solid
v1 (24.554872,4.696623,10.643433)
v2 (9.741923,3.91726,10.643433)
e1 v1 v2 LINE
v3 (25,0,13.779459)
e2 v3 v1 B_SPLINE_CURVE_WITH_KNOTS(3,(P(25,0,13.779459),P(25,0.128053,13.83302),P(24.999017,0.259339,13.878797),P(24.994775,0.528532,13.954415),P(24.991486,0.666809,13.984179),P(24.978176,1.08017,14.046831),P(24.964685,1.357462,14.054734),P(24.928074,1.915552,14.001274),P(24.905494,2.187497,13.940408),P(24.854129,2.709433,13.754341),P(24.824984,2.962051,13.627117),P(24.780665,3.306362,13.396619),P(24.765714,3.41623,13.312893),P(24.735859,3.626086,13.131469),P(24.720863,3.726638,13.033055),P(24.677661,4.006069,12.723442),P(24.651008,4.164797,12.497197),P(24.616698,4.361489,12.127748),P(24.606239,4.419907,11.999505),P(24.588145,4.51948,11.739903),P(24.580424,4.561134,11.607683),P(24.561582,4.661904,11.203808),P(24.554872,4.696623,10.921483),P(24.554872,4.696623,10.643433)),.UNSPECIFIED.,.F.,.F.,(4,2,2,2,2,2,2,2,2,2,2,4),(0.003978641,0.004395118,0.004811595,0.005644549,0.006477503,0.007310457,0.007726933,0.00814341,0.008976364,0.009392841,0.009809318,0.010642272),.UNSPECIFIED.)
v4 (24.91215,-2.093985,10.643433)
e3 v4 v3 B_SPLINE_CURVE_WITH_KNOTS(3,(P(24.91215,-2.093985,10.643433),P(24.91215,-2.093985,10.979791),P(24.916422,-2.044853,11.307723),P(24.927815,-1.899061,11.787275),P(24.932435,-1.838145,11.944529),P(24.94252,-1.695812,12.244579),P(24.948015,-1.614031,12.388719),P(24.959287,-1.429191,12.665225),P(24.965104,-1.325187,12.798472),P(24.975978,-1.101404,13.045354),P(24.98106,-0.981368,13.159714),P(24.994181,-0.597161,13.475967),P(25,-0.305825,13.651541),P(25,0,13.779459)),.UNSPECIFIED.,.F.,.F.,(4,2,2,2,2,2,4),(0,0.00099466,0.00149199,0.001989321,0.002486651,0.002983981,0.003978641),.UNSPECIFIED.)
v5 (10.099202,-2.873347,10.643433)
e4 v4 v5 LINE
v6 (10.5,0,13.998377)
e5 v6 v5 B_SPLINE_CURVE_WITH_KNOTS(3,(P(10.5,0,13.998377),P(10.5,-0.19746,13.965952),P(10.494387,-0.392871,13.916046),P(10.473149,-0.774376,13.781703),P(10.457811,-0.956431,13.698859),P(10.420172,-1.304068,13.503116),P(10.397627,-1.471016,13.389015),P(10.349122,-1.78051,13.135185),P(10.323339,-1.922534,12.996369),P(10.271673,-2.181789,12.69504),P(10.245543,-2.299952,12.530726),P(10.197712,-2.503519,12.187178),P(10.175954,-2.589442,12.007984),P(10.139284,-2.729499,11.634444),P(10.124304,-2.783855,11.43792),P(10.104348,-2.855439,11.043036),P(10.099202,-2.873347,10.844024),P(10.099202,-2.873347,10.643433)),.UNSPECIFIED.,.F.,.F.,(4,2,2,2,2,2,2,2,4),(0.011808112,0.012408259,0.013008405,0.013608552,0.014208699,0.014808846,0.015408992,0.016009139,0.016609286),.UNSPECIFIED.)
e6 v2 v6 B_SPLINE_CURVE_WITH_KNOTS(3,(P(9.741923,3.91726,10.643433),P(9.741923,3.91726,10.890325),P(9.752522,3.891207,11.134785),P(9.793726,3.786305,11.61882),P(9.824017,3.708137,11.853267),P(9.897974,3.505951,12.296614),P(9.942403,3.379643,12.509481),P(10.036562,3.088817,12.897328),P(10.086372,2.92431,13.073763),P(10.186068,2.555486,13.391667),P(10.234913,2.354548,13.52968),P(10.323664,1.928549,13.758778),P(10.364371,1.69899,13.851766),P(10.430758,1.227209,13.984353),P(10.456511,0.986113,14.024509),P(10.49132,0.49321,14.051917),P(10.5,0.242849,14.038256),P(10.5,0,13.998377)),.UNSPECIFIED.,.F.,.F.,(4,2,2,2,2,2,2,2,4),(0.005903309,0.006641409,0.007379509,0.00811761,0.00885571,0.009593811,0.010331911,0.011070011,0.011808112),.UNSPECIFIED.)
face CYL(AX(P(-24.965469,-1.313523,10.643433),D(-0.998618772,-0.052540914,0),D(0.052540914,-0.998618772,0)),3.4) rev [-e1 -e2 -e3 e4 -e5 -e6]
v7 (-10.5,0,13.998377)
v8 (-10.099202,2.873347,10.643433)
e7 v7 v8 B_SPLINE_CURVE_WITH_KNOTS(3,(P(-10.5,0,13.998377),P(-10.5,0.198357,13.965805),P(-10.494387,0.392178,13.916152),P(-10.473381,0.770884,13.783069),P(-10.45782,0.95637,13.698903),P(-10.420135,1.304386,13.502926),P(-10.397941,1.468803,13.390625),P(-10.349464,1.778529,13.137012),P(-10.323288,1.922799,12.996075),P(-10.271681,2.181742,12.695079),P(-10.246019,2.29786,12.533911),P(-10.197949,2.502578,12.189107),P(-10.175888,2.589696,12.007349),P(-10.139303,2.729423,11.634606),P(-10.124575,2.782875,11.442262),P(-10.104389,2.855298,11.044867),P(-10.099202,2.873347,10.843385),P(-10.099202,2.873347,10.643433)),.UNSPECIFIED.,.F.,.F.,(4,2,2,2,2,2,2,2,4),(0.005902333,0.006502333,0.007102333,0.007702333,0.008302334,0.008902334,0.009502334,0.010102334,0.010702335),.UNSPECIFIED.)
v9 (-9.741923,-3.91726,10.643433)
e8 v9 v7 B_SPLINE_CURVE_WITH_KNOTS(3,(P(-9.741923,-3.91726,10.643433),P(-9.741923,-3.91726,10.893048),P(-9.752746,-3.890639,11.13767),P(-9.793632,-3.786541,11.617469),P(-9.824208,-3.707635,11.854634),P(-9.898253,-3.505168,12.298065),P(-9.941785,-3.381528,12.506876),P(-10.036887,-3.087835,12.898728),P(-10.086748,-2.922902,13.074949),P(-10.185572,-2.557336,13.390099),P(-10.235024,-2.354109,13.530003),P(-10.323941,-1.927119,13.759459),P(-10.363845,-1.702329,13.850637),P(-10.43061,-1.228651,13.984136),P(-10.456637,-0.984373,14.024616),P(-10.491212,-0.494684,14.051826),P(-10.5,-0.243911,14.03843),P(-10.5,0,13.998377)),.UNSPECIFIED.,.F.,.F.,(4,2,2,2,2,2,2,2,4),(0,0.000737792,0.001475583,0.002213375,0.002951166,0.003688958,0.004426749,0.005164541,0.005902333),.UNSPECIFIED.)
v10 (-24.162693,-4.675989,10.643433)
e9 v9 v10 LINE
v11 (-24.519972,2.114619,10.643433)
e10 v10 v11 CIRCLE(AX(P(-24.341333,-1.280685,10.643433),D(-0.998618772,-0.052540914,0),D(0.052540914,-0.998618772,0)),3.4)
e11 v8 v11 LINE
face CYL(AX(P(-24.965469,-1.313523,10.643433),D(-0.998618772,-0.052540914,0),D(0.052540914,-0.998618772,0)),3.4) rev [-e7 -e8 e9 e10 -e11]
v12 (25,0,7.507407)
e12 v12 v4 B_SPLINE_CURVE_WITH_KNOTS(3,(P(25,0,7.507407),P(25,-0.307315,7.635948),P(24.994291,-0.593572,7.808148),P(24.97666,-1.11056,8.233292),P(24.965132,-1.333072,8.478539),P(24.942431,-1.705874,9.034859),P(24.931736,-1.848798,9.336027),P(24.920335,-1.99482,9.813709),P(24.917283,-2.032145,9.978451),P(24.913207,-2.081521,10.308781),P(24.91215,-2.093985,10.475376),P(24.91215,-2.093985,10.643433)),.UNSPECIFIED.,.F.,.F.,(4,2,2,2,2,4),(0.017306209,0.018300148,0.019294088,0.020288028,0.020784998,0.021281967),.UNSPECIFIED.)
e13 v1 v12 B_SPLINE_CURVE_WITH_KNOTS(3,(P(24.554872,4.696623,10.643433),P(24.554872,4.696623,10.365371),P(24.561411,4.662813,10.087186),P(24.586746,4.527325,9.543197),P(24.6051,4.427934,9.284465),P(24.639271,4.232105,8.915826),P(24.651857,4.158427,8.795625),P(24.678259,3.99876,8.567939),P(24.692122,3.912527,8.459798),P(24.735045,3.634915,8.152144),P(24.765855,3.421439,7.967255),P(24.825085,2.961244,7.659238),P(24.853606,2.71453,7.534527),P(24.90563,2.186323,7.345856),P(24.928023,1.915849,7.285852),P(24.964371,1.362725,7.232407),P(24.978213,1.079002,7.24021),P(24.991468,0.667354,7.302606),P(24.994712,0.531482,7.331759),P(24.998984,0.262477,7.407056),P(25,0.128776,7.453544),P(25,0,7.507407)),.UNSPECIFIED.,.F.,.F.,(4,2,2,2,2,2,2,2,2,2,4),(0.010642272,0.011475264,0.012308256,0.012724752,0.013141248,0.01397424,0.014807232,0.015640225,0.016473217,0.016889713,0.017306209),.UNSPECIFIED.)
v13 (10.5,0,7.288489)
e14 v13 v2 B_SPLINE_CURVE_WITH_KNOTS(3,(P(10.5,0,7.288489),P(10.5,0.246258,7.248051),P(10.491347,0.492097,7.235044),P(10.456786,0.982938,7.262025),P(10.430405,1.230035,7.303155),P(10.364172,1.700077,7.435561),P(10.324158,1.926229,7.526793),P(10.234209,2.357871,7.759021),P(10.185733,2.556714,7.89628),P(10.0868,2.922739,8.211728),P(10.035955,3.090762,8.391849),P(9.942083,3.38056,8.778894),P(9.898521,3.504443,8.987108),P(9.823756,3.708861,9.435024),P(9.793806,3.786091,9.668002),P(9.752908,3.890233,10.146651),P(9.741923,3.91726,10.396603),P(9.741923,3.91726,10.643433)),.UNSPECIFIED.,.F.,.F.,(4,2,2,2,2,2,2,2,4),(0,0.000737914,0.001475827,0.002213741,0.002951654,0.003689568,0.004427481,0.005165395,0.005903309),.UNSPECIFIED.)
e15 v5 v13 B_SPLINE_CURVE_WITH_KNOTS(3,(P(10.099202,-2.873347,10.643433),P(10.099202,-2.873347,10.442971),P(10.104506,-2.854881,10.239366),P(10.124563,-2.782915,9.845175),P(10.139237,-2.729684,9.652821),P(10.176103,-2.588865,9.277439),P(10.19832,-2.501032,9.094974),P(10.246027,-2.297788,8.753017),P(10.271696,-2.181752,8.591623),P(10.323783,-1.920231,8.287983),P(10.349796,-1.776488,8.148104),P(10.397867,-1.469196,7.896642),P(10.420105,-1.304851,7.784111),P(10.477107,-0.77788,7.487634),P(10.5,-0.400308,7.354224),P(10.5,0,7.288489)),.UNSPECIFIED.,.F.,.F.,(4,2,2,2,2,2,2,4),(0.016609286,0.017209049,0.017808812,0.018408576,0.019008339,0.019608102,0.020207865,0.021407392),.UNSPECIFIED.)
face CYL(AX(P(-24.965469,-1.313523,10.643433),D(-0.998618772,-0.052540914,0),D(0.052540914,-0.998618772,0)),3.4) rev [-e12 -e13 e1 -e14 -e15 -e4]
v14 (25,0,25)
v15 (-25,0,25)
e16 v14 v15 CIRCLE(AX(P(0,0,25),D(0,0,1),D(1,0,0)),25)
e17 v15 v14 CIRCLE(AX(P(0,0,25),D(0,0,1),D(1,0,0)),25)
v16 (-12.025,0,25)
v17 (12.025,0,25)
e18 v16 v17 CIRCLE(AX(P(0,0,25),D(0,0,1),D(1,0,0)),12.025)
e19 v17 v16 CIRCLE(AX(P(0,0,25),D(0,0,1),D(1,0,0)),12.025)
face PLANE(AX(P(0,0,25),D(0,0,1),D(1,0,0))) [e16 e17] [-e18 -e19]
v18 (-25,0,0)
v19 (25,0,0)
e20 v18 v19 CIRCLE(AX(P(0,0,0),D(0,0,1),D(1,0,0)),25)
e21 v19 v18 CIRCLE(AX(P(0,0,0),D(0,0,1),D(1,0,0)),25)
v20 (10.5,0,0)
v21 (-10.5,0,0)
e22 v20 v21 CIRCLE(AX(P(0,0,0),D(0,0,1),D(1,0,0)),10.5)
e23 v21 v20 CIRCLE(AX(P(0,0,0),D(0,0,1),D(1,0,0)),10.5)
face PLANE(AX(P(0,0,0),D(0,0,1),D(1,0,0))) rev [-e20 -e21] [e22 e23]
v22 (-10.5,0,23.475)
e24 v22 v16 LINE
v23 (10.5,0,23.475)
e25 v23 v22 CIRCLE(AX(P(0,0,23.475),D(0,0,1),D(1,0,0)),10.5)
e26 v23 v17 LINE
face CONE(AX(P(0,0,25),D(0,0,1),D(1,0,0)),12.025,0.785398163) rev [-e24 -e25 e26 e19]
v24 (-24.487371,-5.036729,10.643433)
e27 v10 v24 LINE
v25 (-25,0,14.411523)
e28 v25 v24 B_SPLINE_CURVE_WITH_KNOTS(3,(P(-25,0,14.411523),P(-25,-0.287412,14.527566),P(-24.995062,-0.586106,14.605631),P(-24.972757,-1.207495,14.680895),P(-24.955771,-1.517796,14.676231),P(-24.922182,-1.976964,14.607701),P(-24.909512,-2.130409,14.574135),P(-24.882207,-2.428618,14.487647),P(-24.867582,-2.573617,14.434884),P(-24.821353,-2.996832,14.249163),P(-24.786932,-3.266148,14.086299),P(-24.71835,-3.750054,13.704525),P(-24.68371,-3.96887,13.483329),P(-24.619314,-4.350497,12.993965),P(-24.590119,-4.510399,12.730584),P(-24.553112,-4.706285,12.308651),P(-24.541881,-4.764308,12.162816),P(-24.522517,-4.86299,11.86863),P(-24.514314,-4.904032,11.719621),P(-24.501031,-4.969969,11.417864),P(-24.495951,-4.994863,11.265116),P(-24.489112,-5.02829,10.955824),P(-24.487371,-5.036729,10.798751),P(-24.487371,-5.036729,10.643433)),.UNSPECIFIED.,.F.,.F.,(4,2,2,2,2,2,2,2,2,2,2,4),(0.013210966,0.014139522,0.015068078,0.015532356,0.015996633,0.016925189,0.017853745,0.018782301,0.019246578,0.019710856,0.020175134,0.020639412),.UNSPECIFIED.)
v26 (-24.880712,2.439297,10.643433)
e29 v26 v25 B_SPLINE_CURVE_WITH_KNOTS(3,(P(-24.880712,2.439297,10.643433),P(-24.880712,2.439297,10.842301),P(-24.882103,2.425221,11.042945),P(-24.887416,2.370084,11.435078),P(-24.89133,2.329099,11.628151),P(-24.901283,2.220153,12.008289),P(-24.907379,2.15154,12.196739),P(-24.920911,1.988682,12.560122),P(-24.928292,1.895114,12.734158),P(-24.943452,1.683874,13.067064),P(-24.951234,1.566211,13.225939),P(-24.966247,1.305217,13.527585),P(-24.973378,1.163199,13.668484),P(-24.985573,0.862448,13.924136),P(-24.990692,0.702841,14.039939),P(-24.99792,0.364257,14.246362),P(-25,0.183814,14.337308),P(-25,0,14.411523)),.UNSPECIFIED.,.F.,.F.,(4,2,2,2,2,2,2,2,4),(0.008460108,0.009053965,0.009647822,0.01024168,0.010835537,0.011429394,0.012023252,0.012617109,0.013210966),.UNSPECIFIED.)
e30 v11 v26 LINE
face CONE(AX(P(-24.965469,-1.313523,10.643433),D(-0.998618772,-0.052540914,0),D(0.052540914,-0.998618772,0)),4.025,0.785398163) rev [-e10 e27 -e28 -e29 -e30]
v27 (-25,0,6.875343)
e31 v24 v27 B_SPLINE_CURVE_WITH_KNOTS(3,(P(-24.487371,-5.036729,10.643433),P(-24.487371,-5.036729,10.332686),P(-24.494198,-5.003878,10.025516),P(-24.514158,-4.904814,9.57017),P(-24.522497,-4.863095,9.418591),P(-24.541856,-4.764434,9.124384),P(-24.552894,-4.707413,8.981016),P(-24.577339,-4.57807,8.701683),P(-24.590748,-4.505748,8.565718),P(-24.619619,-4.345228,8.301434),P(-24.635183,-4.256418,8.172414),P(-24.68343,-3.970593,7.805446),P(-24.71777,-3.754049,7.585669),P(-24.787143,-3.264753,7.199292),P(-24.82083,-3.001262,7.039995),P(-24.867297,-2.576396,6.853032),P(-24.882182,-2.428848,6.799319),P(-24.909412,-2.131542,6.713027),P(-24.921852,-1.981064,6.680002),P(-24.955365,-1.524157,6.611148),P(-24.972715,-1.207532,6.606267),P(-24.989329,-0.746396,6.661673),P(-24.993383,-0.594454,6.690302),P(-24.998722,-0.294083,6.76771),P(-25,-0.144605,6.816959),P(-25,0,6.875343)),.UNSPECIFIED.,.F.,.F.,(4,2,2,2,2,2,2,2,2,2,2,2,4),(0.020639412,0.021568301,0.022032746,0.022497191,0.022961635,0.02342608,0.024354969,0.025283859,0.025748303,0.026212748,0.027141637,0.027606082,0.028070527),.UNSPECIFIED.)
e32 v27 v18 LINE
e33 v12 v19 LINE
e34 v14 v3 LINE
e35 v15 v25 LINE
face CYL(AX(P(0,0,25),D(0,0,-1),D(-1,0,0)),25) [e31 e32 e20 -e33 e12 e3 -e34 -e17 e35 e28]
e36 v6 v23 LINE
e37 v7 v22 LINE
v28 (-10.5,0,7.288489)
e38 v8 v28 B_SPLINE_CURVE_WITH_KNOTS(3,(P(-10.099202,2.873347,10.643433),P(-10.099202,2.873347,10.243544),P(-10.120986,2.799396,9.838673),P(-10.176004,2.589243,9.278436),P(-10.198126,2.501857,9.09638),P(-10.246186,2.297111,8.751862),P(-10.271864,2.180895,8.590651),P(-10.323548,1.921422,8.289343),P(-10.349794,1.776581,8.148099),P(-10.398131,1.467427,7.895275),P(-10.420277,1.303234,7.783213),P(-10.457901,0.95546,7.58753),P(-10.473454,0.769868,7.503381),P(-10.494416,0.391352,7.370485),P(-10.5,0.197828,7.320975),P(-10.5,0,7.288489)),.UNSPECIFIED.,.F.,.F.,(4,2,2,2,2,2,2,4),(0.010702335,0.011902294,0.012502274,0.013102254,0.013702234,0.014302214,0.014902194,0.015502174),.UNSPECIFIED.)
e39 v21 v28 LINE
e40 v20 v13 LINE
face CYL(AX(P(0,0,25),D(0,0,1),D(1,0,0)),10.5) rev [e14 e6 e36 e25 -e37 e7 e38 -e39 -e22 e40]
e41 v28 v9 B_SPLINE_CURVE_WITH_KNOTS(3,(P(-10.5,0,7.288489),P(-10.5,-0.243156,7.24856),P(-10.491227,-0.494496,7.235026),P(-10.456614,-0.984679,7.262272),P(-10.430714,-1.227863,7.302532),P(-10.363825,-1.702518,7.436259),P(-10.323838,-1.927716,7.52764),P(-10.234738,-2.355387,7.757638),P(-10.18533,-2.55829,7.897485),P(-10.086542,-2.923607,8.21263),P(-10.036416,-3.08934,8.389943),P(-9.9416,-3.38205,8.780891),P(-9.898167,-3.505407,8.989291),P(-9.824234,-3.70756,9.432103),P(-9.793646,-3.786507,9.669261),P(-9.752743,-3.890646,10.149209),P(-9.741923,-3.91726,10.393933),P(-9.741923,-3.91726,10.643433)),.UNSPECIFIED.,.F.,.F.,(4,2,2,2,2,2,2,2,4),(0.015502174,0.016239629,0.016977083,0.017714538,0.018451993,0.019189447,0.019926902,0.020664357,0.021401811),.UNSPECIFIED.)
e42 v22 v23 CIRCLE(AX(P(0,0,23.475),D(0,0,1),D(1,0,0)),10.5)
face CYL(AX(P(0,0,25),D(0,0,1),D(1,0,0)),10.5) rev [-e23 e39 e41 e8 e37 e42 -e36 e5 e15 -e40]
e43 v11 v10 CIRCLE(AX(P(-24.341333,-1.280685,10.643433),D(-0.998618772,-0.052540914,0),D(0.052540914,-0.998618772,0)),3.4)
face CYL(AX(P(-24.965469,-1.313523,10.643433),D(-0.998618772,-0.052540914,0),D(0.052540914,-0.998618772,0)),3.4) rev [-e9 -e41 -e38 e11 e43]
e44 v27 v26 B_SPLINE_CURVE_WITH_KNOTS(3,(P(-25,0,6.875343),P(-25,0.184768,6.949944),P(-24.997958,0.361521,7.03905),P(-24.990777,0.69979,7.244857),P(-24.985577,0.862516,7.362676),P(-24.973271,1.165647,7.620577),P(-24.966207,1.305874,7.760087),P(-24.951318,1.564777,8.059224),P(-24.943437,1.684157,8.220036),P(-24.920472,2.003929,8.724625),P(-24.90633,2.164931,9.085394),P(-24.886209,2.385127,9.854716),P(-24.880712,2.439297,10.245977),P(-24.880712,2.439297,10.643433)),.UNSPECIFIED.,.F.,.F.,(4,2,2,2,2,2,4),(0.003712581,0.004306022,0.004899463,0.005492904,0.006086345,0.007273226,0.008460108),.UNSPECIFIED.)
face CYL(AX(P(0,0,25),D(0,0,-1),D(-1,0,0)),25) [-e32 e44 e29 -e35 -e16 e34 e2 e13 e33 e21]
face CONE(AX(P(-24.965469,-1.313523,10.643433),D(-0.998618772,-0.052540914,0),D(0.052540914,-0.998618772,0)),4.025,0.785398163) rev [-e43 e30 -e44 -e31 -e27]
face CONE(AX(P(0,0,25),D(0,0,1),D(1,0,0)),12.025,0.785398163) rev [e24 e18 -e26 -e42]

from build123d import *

# Parameters (mm, degrees)
SKETCH1_R                    = 25
BOSS_EXTRUDE1_DEPTH          = 25
M24_TAPPED_HOLE1_D           = 21
M24_TAPPED_HOLE1_DEPTH       = 57
M24_TAPPED_HOLE1_CSINK_D     = 24.05
M24_TAPPED_HOLE1_CSINK_ANGLE = 90
M24_TAPPED_HOLE1_TIP         = 6.3090365
M8_TAPPED_HOLE1_D            = 6.8
M8_TAPPED_HOLE1_DEPTH        = 63.75
M8_TAPPED_HOLE1_CSINK_D      = 8.05
M8_TAPPED_HOLE1_CSINK_ANGLE  = 90
M8_TAPPED_HOLE1_TIP          = 2.042926105


with BuildPart() as part:
    # Sketch1 → Boss-Extrude1 (new body)
    with BuildSketch(Plane.XY):
        Circle(SKETCH1_R)
    extrude(amount=BOSS_EXTRUDE1_DEPTH)

    # M24 Tapped Hole1
    with Locations(Plane.XY.offset(25)):
        with Locations((0, 0)):
            CounterSinkHole(M24_TAPPED_HOLE1_D / 2, M24_TAPPED_HOLE1_CSINK_D / 2, depth=M24_TAPPED_HOLE1_DEPTH, counter_sink_angle=M24_TAPPED_HOLE1_CSINK_ANGLE)
            with Locations((0, 0, -(M24_TAPPED_HOLE1_DEPTH + M24_TAPPED_HOLE1_TIP / 2))):  # 118° drill point
                Cone(0, M24_TAPPED_HOLE1_D / 2, M24_TAPPED_HOLE1_TIP, mode=Mode.SUBTRACT)

    # M8 Tapped Hole1
    with Locations(Plane(origin=(-24.965469306, -1.313522862, 10.643433194), x_dir=(0.052540914496, -0.998618772257, 0), z_dir=(-0.998618772257, -0.052540914496, 0))):
        with Locations((0, 0)):
            CounterSinkHole(M8_TAPPED_HOLE1_D / 2, M8_TAPPED_HOLE1_CSINK_D / 2, depth=M8_TAPPED_HOLE1_DEPTH, counter_sink_angle=M8_TAPPED_HOLE1_CSINK_ANGLE)
            with Locations((0, 0, -(M8_TAPPED_HOLE1_DEPTH + M8_TAPPED_HOLE1_TIP / 2))):  # 118° drill point
                Cone(0, M8_TAPPED_HOLE1_D / 2, M8_TAPPED_HOLE1_TIP, mode=Mode.SUBTRACT)


solid = part.part
